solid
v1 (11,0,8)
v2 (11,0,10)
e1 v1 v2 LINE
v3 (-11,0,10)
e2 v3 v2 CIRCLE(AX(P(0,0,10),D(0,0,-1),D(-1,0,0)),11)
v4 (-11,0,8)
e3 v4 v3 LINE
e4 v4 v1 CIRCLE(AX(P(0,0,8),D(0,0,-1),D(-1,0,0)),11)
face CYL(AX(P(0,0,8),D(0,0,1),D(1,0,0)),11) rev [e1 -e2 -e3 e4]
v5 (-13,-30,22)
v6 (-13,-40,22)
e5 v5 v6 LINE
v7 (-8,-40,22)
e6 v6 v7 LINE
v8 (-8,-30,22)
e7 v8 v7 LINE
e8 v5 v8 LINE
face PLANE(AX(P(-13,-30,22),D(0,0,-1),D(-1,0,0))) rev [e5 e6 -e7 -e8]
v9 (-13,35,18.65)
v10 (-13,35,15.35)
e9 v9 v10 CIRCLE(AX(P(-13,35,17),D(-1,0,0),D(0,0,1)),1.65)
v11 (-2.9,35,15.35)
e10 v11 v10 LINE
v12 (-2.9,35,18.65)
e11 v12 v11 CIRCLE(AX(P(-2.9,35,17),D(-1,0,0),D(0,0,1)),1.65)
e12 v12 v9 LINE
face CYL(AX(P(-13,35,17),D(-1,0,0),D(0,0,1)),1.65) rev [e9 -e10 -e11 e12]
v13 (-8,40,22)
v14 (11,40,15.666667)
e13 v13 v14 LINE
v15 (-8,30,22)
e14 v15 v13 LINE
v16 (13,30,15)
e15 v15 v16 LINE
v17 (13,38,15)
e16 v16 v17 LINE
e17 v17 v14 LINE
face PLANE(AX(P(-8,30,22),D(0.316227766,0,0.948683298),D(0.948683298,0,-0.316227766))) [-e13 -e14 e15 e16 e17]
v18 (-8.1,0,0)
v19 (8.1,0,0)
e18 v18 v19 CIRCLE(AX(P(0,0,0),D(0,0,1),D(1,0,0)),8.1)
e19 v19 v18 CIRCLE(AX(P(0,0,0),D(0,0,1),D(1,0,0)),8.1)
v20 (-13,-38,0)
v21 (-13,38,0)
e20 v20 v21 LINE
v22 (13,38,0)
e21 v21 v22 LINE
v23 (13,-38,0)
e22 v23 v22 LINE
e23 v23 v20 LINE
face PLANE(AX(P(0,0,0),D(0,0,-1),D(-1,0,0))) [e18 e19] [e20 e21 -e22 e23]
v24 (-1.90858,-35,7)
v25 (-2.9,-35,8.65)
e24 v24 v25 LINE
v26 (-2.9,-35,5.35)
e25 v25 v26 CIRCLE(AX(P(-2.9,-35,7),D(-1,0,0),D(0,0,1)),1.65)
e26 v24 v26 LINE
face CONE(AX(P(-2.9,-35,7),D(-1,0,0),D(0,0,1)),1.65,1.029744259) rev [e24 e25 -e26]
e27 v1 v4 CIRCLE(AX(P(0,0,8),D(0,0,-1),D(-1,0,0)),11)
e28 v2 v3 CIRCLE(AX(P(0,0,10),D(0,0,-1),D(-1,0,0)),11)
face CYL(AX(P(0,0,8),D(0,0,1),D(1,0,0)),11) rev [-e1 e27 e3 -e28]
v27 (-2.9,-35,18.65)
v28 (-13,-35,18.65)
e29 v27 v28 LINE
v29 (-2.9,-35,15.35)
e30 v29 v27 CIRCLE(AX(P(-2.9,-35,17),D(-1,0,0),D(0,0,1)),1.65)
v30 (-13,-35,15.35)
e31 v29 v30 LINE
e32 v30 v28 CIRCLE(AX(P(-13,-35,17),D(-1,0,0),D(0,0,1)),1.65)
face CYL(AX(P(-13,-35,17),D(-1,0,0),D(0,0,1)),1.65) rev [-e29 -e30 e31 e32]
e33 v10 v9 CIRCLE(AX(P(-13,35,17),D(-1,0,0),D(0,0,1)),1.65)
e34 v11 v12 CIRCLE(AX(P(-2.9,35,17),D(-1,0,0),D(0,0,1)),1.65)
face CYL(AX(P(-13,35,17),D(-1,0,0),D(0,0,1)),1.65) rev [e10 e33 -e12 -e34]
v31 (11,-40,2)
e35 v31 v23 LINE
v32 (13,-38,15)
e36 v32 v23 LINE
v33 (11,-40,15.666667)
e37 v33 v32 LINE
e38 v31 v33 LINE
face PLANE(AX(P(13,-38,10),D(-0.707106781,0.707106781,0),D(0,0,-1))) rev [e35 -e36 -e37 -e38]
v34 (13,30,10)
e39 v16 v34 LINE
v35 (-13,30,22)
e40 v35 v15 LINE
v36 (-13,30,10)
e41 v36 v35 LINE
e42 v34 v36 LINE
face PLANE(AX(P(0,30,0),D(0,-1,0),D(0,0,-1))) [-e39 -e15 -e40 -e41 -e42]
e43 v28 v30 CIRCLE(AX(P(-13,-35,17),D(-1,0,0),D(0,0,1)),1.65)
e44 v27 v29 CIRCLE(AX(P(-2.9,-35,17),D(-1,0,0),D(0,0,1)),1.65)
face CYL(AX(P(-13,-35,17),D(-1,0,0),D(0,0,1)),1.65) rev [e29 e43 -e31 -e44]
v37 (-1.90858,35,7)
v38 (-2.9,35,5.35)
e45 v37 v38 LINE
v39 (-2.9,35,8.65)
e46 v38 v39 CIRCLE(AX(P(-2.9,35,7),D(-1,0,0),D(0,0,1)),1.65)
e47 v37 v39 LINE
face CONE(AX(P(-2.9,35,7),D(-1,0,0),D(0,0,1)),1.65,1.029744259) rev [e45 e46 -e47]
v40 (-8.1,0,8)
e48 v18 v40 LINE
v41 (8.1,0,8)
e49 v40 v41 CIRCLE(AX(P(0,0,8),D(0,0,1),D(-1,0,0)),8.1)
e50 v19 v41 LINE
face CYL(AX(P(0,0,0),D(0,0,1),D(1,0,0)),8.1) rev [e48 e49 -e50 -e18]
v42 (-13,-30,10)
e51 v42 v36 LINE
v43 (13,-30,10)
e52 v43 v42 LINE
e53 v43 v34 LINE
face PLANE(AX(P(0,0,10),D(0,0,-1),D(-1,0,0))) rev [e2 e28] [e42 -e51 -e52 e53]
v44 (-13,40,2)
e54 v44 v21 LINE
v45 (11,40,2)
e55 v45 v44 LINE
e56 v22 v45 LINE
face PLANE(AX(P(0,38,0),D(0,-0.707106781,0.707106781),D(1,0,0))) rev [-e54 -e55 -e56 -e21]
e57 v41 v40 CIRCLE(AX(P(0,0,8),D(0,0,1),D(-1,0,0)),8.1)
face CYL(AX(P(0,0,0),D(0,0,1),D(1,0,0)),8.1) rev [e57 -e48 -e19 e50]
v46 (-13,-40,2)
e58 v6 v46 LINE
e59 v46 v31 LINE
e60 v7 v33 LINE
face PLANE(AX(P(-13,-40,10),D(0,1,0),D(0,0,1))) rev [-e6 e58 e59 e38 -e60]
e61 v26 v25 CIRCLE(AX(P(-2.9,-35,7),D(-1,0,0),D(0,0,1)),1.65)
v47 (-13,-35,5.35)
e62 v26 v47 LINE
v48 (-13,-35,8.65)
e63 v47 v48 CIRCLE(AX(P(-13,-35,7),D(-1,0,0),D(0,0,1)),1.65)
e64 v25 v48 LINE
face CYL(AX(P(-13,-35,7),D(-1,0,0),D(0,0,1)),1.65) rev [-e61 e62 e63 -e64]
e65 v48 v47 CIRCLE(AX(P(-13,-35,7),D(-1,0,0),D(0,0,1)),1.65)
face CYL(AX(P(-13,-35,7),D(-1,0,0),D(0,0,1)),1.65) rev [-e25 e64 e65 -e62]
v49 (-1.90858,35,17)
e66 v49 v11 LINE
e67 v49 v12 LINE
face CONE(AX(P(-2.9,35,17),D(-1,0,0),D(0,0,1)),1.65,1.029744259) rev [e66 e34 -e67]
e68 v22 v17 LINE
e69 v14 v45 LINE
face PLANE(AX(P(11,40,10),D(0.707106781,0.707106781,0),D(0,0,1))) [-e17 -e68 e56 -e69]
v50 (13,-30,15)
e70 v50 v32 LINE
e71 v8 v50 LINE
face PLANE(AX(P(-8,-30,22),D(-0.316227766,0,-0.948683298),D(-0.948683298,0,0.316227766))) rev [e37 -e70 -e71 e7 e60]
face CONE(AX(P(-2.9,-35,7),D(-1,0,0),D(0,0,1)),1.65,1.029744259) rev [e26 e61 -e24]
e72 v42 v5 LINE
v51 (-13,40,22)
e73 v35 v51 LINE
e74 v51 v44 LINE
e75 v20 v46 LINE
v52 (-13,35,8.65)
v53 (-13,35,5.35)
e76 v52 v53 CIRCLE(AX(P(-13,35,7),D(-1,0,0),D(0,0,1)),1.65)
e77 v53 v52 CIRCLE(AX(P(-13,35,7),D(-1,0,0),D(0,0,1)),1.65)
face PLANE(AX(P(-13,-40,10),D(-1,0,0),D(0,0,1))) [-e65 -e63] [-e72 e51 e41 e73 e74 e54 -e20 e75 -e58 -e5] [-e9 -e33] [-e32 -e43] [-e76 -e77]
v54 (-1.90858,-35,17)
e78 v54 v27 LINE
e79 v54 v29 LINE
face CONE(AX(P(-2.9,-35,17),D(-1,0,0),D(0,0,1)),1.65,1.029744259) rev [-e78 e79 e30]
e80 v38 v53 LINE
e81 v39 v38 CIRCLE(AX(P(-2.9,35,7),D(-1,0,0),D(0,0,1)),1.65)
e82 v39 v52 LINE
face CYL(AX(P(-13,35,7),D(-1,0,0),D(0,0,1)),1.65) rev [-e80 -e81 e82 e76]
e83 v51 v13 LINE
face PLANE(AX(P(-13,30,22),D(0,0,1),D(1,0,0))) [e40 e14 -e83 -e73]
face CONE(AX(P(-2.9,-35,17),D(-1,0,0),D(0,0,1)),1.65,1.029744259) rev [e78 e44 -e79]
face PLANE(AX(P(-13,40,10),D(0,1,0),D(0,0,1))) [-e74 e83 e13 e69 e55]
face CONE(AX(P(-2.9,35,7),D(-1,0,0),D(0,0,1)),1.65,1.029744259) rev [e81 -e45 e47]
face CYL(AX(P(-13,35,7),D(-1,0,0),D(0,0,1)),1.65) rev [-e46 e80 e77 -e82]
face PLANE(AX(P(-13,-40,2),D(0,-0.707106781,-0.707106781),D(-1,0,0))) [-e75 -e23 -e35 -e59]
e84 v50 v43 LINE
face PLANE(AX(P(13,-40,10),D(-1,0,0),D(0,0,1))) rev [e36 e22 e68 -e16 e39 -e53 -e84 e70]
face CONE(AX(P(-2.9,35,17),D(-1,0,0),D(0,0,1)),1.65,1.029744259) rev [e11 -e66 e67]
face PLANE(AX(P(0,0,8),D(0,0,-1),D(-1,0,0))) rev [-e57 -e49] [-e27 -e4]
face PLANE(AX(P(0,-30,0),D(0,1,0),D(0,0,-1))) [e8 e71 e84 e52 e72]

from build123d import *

# Parameters (mm, degrees)
SKETCH_1_W             = 26
SKETCH_1_H             = 80
EXTRUDE_1_DEPTH        = 10
SKETCH_2_R             = 8.1
CUT_EXTRUDE_1_DEPTH    = 44.231932642
EXTRUDE_2_DEPTH        = 10
CHAMFER_1_SIZE         = 2
CHAMFER_2_SIZE         = 2
SKETCH_9_R             = 11
CUT_EXTRUDE_2_DEPTH    = 2
HOLE_WIZARD_M4_1_D     = 3.3
HOLE_WIZARD_M4_1_DEPTH = 10.1
HOLE_WIZARD_M4_1_TIP   = 0.991420021


with BuildPart() as part:
    # 草图1 → 凸台-拉伸1 (new body)
    with BuildSketch(Plane.XY):
        Rectangle(SKETCH_1_W, SKETCH_1_H)
    extrude(amount=EXTRUDE_1_DEPTH)

    # 草图2 → 切除-拉伸1 (cut, through all)
    with BuildSketch(Plane.XY.offset(10)):
        Circle(SKETCH_2_R)
    extrude(amount=-CUT_EXTRUDE_1_DEPTH, mode=Mode.SUBTRACT)

    # 草图7 → 凸台-拉伸2 (add)
    with BuildSketch(Plane(origin=(0, 40, 0), x_dir=(1, 0, 0), z_dir=(0, 1, 0))):
        Polygon((13, -10), (13, -15), (-8, -22), (-13, -22), (-13, -10), align=None)
    extrude_2 = extrude(amount=-EXTRUDE_2_DEPTH)

    # 镜向1: 凸台-拉伸2 across plane
    add(extrude_2.mirror(Plane.ZX))

    # 倒角1
    chamfer_1_edges = [part.edges().sort_by_distance(p)[0] for p in [
        (13, -40, 7.5),
        (13, 40, 7.5),
    ]]
    chamfer(chamfer_1_edges, length=CHAMFER_1_SIZE)

    # 倒角2
    chamfer_2_edges = [part.edges().sort_by_distance(p)[0] for p in [
        (-1, -40, 0),
        (-1, 40, 0),
    ]]
    chamfer(chamfer_2_edges, length=CHAMFER_2_SIZE)

    # 草图9 → 切除-拉伸2 (cut)
    with BuildSketch(Plane(origin=(0, 0, 10), x_dir=(-1, 0, 0), z_dir=(0, 0, -1))):
        Circle(SKETCH_9_R)
    extrude(amount=CUT_EXTRUDE_2_DEPTH, mode=Mode.SUBTRACT)

    # M4 螺纹孔1
    with Locations(Plane.ZY.offset(13)):
        with Locations((17, 35), (7, 35), (7, -35), (17, -35)):
            Hole(HOLE_WIZARD_M4_1_D / 2, depth=HOLE_WIZARD_M4_1_DEPTH)
            with Locations((0, 0, -(HOLE_WIZARD_M4_1_DEPTH + HOLE_WIZARD_M4_1_TIP / 2))):  # 118° drill point
                Cone(0, HOLE_WIZARD_M4_1_D / 2, HOLE_WIZARD_M4_1_TIP, mode=Mode.SUBTRACT)


solid = part.part
